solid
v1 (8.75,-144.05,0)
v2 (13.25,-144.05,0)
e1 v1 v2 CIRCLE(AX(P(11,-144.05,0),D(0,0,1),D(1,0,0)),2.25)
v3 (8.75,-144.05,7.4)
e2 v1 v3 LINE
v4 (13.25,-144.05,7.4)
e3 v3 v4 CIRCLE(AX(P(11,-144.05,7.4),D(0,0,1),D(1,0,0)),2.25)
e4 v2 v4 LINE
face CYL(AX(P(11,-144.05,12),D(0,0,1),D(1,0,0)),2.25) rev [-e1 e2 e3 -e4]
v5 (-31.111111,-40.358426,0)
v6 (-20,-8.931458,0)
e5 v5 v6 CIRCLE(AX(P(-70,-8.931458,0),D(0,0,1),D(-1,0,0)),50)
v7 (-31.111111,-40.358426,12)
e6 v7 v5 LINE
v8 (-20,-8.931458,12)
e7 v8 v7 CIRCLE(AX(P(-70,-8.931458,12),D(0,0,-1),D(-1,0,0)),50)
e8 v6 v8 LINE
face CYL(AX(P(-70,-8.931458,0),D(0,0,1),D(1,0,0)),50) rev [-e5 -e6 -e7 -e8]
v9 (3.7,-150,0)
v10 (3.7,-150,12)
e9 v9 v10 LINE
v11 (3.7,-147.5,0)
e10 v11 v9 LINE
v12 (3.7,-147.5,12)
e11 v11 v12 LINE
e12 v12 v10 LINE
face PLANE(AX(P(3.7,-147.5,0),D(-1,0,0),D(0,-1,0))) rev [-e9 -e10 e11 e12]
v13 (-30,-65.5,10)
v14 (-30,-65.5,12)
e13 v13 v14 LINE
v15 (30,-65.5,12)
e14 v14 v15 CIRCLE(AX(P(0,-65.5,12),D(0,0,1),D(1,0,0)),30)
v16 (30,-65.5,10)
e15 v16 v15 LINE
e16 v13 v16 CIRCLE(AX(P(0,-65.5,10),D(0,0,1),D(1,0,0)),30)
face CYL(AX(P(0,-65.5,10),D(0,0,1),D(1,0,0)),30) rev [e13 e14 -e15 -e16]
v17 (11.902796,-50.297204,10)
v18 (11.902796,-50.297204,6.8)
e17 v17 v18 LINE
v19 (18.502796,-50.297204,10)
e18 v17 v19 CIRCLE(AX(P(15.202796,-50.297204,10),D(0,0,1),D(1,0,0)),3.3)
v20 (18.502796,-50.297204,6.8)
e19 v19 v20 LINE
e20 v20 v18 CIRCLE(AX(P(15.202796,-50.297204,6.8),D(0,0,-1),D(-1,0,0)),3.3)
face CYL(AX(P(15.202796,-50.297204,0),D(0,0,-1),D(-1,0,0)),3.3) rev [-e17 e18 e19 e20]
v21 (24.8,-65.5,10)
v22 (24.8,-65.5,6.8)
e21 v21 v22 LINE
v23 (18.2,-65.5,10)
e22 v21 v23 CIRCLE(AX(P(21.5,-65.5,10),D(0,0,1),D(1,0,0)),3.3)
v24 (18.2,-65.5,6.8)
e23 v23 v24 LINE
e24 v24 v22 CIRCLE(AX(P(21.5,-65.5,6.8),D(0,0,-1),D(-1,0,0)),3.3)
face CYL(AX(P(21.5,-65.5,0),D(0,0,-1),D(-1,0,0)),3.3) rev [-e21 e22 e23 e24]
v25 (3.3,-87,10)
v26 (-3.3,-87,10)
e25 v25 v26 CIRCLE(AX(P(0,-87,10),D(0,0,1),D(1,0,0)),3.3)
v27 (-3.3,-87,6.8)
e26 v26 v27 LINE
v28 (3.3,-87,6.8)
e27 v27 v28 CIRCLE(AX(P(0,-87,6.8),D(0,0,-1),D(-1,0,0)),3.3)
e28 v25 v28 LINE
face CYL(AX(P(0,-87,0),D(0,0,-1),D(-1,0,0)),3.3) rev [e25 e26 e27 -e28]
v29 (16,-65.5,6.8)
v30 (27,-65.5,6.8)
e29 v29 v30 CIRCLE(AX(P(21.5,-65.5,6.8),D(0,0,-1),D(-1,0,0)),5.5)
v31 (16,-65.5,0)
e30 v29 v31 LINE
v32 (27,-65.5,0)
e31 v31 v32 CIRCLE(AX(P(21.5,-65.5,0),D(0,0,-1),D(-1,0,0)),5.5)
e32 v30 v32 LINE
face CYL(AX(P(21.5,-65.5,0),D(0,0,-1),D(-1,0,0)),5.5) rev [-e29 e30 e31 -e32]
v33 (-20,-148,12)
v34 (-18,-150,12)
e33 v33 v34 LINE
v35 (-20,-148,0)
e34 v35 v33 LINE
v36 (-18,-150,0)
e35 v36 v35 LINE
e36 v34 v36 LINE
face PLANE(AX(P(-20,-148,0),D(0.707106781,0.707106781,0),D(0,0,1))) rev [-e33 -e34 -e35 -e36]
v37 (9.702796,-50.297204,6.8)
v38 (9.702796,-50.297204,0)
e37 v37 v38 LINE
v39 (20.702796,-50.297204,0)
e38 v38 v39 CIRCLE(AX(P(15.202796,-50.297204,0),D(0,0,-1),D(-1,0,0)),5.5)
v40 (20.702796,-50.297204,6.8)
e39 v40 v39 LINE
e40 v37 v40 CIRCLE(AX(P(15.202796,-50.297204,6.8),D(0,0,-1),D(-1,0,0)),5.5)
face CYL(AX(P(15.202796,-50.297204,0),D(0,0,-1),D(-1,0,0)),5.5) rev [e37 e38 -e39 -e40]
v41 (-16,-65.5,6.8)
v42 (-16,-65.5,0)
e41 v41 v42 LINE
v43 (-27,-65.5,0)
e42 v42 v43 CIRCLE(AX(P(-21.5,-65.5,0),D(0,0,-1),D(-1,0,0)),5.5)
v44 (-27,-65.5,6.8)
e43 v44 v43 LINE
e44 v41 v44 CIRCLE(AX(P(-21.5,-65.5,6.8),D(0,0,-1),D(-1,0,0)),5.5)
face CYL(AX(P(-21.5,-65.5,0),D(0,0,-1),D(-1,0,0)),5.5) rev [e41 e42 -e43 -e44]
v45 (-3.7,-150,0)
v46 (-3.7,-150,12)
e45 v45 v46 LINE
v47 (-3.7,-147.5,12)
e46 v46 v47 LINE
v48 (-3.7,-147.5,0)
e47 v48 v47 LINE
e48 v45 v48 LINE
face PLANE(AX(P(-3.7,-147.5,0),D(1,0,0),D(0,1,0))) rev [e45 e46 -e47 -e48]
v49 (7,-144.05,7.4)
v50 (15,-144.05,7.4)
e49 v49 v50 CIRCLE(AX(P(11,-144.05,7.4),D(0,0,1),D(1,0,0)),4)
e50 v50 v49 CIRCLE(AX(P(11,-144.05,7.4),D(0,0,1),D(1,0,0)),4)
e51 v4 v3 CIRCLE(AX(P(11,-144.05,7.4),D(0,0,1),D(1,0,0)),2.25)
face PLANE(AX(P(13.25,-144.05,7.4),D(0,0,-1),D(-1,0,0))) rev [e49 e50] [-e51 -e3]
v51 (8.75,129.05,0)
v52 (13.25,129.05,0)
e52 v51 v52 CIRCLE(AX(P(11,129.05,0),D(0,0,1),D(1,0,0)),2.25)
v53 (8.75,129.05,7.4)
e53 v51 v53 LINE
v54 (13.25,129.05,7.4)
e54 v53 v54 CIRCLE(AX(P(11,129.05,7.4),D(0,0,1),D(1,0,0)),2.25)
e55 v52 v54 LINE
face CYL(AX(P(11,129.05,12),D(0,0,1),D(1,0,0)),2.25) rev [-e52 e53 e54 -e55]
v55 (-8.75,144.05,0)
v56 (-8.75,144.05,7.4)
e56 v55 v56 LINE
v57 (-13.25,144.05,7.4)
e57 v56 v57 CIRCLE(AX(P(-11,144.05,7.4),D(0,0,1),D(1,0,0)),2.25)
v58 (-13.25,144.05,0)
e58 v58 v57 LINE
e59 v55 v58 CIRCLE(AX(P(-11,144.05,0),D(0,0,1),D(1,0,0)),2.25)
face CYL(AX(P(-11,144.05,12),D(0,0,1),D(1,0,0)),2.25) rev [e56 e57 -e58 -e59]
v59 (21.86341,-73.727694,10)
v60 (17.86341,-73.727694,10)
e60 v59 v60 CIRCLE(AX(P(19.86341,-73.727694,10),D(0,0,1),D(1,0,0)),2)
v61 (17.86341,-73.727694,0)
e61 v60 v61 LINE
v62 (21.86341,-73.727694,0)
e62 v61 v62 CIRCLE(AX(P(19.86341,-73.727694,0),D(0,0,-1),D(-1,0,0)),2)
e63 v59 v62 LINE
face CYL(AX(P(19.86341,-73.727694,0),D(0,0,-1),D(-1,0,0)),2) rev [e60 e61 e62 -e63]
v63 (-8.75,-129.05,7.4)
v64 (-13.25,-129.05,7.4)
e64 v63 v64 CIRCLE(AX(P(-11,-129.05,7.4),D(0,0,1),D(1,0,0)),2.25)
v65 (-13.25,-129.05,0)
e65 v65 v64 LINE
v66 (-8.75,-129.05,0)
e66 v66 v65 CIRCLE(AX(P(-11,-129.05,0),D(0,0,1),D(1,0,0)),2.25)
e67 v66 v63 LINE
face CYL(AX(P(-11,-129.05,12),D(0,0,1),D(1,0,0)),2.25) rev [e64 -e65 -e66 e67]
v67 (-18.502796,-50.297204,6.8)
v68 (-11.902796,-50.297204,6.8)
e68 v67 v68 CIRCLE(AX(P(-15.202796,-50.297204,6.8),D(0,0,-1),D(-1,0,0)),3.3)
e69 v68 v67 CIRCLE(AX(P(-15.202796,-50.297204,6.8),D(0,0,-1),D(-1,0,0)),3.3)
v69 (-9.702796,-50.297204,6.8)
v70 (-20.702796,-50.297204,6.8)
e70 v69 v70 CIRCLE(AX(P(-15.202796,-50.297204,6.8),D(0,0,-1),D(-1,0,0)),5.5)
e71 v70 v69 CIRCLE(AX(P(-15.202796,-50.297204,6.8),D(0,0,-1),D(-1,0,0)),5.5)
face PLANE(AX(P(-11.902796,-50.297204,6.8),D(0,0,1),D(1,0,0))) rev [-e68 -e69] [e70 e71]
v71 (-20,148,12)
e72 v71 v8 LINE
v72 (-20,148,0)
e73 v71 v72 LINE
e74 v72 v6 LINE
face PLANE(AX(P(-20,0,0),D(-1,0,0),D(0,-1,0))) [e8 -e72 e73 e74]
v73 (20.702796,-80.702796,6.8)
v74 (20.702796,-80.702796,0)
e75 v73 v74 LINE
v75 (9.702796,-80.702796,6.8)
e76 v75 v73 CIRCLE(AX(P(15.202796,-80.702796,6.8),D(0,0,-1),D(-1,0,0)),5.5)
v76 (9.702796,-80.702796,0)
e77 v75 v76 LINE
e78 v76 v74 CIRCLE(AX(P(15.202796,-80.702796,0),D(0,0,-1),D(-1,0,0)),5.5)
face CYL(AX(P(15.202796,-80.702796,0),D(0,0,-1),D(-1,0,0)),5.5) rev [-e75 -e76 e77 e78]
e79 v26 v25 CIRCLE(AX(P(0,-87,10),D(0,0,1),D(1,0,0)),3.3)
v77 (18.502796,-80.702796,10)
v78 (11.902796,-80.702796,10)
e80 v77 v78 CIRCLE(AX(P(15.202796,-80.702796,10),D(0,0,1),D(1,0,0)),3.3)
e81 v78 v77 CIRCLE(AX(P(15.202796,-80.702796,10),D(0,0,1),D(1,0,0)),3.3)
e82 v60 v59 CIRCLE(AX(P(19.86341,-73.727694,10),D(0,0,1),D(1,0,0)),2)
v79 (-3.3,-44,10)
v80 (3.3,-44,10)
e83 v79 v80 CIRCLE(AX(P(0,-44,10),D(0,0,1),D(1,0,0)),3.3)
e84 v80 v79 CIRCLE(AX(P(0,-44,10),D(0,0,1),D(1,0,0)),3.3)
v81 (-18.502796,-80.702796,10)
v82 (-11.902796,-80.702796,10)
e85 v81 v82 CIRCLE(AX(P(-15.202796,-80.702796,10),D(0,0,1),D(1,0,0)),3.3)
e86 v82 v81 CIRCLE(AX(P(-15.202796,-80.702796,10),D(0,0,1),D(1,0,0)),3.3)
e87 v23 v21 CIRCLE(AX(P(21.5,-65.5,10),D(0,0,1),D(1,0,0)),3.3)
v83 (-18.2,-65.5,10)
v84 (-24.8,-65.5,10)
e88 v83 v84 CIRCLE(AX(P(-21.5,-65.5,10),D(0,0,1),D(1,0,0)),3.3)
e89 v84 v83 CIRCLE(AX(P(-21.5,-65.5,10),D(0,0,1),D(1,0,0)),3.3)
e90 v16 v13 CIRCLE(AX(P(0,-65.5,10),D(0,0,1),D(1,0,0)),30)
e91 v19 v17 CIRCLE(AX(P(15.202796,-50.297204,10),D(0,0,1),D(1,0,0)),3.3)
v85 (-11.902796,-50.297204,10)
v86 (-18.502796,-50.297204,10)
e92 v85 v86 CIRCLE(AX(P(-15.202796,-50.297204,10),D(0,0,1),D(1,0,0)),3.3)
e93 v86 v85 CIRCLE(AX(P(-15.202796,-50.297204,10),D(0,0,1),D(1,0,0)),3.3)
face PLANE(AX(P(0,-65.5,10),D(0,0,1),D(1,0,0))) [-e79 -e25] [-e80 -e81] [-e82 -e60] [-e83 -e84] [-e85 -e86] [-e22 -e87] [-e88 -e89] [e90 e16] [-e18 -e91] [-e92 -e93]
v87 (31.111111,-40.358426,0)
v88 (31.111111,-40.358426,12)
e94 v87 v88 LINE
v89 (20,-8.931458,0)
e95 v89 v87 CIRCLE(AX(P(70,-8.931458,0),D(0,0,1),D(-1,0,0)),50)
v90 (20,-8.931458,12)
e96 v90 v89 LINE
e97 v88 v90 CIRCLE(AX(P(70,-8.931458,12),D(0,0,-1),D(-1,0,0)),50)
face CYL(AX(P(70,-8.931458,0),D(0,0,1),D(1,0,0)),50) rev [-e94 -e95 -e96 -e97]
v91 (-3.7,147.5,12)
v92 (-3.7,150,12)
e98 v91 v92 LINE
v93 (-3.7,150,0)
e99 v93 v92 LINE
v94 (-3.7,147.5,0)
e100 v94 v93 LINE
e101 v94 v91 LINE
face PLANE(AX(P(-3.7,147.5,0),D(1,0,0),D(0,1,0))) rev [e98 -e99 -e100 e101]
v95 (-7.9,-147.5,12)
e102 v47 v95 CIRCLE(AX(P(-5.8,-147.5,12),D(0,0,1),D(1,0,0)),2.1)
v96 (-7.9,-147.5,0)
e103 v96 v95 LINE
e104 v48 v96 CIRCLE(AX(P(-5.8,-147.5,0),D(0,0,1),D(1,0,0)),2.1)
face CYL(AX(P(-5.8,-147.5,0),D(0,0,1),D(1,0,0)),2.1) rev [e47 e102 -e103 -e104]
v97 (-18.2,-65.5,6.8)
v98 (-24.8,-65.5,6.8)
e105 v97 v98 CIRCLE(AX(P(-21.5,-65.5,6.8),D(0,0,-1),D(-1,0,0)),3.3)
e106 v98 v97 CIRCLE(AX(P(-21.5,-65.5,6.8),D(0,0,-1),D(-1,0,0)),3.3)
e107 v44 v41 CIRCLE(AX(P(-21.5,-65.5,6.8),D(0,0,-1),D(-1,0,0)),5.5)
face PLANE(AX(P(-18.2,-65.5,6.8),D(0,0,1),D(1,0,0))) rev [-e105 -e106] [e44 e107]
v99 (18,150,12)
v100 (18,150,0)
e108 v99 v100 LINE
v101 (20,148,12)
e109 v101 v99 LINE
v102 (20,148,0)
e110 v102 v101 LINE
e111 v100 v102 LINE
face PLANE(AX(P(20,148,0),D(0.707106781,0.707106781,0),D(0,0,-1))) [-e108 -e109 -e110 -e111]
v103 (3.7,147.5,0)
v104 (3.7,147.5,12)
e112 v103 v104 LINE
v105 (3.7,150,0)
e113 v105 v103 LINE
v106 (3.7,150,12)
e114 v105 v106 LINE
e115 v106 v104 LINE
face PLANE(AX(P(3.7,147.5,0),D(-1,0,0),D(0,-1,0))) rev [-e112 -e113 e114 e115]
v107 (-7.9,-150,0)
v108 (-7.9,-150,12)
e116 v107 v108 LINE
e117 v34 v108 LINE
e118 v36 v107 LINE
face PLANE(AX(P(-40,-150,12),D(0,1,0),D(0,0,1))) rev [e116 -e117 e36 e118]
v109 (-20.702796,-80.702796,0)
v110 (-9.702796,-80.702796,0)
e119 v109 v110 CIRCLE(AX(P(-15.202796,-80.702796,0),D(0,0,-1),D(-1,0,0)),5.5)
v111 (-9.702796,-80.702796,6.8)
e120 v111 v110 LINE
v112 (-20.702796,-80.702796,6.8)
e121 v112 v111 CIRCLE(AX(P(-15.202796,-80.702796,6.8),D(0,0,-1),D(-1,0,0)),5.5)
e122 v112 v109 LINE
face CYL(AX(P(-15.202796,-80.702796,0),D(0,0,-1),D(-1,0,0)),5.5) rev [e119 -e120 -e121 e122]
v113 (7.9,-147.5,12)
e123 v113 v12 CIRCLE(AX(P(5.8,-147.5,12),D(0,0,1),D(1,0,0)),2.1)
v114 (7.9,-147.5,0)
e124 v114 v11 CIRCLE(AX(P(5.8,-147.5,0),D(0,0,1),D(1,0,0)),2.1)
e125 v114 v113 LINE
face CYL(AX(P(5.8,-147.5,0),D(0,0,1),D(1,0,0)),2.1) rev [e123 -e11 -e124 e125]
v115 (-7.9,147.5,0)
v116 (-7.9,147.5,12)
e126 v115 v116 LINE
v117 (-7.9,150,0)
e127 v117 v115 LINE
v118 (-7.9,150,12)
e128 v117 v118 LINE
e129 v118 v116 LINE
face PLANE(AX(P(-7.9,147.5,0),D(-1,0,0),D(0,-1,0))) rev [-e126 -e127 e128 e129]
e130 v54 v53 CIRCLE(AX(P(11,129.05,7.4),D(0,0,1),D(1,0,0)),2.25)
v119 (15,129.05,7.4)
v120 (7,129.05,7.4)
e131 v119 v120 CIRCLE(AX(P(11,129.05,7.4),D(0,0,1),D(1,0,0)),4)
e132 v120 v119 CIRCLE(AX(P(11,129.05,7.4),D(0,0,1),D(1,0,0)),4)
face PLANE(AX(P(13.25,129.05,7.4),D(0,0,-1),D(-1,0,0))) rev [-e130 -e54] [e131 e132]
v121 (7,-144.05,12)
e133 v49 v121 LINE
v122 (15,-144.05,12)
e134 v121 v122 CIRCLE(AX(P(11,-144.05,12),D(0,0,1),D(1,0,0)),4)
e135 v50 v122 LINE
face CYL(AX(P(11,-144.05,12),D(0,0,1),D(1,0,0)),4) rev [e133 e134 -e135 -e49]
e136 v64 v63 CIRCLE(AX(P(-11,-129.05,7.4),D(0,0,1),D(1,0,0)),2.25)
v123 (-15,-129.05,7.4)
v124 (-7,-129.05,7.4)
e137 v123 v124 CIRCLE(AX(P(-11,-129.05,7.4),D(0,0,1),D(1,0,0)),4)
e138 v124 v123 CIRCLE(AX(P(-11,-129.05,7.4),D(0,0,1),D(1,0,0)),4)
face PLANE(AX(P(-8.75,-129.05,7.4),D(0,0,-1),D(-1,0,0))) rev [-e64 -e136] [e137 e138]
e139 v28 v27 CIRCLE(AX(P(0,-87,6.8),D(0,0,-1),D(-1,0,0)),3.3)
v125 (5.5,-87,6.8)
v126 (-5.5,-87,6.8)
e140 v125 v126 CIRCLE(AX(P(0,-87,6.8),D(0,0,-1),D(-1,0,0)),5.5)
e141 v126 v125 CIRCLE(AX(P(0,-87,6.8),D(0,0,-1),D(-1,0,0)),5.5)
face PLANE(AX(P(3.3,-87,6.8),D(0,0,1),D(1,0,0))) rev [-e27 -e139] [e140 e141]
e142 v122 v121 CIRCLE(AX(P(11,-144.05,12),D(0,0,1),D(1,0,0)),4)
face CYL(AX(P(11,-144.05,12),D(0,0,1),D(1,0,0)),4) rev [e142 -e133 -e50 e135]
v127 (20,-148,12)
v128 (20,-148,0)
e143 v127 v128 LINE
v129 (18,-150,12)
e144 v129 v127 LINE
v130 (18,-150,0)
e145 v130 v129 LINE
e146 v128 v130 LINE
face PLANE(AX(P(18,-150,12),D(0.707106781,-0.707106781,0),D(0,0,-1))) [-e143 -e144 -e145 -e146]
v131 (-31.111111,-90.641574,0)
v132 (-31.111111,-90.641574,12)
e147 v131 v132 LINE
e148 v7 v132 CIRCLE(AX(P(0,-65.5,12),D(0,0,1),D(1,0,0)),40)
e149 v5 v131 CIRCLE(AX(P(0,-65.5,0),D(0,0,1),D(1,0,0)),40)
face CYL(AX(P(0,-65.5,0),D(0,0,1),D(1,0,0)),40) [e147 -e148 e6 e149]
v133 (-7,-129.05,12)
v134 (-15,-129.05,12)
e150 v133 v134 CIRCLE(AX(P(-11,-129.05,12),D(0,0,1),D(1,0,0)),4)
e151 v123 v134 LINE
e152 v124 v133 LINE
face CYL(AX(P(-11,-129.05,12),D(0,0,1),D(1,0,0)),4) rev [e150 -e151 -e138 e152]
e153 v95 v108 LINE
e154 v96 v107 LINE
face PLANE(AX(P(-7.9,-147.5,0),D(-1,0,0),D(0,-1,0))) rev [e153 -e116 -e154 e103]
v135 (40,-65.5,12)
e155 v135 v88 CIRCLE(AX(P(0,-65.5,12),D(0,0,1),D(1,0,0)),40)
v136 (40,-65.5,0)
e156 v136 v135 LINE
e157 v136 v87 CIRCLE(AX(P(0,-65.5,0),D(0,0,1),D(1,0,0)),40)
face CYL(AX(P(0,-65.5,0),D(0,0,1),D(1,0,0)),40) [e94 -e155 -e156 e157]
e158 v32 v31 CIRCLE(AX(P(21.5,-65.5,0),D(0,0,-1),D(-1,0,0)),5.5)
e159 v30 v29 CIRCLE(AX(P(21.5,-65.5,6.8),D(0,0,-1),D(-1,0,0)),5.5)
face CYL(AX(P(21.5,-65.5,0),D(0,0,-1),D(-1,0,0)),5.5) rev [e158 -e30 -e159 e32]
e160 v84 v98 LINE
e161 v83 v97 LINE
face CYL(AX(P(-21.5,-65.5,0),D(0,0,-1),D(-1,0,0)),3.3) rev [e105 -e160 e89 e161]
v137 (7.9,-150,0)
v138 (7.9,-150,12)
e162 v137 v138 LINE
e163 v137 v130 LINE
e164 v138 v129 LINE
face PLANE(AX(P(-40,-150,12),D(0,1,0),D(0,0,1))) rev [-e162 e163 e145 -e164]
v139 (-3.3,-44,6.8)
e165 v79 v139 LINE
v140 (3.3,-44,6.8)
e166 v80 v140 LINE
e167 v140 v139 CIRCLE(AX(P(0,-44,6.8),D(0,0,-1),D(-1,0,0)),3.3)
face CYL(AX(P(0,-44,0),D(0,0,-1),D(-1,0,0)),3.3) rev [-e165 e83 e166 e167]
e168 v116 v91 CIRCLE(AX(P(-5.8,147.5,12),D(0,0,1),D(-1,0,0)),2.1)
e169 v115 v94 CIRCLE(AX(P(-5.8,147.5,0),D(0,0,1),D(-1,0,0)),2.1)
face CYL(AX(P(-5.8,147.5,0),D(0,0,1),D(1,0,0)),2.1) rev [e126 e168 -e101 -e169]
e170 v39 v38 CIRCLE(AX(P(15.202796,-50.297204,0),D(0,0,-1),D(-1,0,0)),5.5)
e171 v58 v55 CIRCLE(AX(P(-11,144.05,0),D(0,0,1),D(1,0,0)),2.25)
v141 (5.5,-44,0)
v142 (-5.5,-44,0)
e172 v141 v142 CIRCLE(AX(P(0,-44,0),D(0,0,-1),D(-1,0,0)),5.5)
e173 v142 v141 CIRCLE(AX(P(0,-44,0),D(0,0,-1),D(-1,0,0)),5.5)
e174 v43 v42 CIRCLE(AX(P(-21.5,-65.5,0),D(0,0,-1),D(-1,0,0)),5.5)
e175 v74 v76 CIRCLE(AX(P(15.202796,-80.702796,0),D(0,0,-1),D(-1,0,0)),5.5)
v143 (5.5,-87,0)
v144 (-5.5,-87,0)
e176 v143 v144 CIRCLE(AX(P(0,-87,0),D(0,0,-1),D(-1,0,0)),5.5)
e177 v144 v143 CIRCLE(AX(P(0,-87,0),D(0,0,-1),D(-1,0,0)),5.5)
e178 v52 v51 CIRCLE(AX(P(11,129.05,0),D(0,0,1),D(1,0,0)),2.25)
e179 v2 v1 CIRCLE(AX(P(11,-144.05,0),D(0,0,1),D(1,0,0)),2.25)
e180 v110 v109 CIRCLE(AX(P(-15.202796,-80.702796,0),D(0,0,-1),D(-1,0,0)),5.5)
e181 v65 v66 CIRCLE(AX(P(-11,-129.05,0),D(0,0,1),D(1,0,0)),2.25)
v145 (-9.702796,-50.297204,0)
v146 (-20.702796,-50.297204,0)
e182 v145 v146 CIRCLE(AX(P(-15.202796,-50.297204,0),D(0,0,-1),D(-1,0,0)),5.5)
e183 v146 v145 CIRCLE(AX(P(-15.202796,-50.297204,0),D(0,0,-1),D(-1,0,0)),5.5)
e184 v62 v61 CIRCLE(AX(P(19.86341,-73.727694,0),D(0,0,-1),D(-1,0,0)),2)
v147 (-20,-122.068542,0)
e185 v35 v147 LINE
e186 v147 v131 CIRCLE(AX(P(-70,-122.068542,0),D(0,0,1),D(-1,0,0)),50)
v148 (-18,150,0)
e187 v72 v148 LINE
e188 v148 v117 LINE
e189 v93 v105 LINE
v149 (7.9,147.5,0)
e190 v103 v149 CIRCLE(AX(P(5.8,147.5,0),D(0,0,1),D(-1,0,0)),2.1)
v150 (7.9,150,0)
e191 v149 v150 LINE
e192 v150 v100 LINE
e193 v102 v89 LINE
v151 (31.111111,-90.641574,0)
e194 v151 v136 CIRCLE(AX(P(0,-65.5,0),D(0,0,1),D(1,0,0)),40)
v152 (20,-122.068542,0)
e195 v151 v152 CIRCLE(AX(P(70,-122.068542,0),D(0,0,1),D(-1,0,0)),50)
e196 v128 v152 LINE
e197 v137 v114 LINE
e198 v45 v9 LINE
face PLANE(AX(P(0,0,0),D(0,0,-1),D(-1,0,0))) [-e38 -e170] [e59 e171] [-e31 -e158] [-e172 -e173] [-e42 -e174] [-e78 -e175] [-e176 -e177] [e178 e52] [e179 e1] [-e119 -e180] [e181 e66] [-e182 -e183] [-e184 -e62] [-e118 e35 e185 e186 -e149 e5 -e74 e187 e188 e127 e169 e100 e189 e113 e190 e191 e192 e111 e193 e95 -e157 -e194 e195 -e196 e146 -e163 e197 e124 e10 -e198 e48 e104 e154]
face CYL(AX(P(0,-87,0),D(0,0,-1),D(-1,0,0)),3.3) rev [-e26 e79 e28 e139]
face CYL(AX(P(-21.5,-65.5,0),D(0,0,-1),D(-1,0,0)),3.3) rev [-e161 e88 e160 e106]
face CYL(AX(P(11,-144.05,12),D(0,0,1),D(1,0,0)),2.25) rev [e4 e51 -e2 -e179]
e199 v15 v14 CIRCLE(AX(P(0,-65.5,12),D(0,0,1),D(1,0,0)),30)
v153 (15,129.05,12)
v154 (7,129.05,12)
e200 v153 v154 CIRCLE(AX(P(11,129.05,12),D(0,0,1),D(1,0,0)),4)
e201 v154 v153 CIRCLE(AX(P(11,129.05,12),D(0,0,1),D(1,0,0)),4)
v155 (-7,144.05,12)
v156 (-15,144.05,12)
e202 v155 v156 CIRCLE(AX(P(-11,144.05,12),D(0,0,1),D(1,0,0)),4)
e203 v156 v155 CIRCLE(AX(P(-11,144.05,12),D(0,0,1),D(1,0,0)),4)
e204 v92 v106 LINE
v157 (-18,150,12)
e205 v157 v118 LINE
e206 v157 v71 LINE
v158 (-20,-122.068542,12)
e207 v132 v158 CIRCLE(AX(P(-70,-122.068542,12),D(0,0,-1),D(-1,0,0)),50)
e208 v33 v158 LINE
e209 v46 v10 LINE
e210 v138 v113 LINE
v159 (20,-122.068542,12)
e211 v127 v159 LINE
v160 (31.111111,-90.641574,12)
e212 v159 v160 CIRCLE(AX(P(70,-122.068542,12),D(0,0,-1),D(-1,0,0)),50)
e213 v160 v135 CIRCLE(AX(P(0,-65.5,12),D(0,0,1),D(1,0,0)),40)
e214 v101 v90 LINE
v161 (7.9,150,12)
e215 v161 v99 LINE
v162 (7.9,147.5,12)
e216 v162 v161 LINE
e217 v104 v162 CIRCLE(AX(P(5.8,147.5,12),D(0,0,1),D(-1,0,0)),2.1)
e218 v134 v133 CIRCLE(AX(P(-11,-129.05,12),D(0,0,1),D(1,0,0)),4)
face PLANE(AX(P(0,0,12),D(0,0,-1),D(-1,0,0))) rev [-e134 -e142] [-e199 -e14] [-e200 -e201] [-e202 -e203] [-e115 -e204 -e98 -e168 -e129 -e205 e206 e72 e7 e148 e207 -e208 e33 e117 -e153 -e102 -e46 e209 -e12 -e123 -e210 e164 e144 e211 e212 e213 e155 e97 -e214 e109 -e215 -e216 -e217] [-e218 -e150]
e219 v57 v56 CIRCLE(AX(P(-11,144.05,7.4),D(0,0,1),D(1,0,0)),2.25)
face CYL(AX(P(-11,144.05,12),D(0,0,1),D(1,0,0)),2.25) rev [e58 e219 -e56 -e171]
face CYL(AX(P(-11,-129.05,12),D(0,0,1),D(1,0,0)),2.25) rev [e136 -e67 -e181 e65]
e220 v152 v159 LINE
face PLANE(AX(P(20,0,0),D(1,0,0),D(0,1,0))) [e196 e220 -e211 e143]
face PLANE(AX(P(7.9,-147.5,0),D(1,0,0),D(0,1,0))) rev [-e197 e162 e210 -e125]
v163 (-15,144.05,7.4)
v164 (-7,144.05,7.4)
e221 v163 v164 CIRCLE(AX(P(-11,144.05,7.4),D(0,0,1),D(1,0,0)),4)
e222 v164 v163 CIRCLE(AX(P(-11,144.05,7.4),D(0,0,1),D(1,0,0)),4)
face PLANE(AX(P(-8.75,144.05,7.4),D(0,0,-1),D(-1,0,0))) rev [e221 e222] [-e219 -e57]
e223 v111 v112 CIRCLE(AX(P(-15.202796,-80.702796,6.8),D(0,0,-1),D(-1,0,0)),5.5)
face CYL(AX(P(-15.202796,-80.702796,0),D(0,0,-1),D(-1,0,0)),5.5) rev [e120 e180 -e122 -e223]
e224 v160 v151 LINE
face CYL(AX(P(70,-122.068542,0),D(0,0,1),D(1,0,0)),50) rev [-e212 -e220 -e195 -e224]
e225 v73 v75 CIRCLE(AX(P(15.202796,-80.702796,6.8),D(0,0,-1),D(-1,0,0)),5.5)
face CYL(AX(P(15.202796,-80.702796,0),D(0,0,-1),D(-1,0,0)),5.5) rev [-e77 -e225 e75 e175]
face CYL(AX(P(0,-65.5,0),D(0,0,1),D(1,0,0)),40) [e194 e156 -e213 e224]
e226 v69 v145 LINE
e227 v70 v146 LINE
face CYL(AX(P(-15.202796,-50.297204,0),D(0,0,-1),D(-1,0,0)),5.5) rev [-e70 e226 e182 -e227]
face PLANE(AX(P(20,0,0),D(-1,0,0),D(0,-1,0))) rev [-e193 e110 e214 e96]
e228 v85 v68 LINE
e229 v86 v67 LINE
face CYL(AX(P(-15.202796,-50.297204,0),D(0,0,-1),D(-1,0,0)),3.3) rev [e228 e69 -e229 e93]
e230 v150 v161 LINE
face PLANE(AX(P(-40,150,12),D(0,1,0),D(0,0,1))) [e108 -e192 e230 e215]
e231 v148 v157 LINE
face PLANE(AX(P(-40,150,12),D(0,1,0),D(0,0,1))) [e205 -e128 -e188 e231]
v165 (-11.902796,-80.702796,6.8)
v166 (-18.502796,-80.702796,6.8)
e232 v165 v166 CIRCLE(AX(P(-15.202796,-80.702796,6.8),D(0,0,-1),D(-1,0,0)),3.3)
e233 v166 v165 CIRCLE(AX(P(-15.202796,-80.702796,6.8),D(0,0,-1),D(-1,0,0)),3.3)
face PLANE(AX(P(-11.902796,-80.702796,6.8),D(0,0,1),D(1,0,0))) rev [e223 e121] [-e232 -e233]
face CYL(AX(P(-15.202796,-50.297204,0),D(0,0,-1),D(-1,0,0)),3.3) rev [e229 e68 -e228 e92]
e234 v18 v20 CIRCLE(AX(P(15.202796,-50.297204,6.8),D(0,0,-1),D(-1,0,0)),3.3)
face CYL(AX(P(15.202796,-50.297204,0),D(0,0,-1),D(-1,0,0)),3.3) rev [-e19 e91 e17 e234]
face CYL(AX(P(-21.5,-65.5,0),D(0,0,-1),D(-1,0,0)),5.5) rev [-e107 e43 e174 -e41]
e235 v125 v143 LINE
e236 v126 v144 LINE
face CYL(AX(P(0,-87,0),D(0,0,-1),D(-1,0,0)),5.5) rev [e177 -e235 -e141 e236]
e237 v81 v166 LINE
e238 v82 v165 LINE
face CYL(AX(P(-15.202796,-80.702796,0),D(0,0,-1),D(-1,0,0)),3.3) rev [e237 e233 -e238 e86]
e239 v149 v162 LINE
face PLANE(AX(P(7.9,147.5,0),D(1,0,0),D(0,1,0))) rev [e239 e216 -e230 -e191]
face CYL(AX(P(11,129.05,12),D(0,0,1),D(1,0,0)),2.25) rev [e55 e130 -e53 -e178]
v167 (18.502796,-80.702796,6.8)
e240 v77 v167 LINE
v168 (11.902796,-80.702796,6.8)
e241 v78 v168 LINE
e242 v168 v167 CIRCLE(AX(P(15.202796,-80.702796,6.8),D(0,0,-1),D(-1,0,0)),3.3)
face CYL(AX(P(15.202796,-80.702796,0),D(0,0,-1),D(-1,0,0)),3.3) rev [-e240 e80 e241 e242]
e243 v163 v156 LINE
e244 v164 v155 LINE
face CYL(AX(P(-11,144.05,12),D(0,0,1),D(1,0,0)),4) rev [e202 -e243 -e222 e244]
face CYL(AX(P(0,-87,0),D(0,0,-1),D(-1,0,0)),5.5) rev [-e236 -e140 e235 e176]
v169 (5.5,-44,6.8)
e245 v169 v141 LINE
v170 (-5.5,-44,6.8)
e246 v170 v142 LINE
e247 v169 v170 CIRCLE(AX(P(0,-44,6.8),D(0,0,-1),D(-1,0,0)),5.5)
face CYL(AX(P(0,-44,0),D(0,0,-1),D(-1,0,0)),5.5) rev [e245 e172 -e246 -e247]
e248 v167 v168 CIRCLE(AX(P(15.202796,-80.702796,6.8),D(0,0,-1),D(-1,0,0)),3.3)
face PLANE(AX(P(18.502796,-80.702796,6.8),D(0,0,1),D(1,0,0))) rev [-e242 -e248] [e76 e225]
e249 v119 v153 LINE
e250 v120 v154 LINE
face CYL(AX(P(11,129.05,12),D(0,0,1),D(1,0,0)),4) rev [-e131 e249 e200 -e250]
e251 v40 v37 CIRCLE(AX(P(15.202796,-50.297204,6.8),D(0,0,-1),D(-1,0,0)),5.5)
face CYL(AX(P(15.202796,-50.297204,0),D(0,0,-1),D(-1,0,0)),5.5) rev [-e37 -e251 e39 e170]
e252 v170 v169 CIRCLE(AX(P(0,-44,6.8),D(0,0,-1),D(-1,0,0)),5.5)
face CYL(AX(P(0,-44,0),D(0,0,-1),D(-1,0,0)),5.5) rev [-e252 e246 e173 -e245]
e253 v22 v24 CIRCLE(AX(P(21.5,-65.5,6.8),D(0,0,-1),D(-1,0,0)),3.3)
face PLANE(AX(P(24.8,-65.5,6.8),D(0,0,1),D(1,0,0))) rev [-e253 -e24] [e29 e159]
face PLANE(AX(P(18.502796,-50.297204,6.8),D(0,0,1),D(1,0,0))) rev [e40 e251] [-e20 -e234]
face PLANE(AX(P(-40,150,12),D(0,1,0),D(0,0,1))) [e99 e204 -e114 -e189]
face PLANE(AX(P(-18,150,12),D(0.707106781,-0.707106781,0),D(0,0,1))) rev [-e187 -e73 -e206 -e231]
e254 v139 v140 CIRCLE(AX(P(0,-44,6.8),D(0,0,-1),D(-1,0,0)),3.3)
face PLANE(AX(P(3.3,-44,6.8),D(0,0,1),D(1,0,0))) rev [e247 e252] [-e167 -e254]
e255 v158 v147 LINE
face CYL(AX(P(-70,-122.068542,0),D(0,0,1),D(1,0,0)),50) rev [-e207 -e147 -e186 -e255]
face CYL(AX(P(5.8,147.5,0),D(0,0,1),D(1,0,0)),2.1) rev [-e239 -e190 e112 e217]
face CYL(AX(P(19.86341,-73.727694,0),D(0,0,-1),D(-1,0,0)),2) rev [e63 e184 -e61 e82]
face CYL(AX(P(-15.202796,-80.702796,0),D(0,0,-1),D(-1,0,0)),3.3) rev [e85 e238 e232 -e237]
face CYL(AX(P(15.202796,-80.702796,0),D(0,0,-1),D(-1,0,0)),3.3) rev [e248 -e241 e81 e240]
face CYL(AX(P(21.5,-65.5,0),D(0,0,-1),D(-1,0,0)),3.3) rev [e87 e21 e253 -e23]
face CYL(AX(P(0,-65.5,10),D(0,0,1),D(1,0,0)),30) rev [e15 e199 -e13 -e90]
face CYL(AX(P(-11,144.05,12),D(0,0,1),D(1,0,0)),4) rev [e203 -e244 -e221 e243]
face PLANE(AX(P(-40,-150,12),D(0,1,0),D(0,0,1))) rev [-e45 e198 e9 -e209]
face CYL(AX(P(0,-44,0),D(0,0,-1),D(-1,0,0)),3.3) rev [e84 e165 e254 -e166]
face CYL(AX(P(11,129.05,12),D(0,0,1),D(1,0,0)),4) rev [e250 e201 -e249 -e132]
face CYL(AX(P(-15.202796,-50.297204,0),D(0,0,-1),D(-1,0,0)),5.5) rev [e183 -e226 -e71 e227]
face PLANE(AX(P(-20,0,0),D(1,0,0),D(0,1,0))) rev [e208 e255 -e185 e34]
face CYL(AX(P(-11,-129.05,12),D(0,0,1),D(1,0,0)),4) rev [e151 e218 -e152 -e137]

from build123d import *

# Parameters (mm, degrees)
SKETCH_1_W                   = 80
SKETCH_1_H                   = 300
EXTRUDE_1_DEPTH              = 12
CHAMFER_1_SIZE               = 2
SKETCH_2_R                   = 30
CUT_EXTRUDE_1_DEPTH          = 2
CUT_EXTRUDE_2_DEPTH          = 156.704848993
FILLET_1_R                   = 50
CHAMFER_3_SIZE               = 2
HOLE_WIZARD_M6_1_D           = 6.6
HOLE_WIZARD_M6_1_CBORE_D     = 11
HOLE_WIZARD_M6_1_CBORE_DEPTH = 6.8
F_4_0MM_1_D                  = 4
HOLE_WIZARD_M4_1_D           = 4.5
HOLE_WIZARD_M4_1_CBORE_D     = 8
HOLE_WIZARD_M4_1_CBORE_DEPTH = 4.6
CUT_EXTRUDE_3_DEPTH          = 156.704848993
PATTERN_CIRCULAR_1_COUNT     = 8


with BuildPart() as part:
    # 草图1 → 凸台-拉伸1 (new body)
    with BuildSketch(Plane.XY):
        Rectangle(SKETCH_1_W, SKETCH_1_H)
    extrude(amount=EXTRUDE_1_DEPTH)

    # 倒角1
    chamfer_1_edges = [part.edges().sort_by_distance(p)[0] for p in [
        (-40, -150, 6),
        (40, -150, 6),
        (40, 150, 6),
        (-40, 150, 6),
    ]]
    chamfer(chamfer_1_edges, length=CHAMFER_1_SIZE)

    # 草图2 → 切除-拉伸1 (cut)
    with BuildSketch(Plane.XY.offset(12)):
        with Locations((0, -65.5)):
            Circle(SKETCH_2_R)
    extrude(amount=-CUT_EXTRUDE_1_DEPTH, mode=Mode.SUBTRACT)

    # 草图3 → 切除-拉伸2 (cut, through all)
    with BuildSketch(Plane.XY.offset(12)):
        with BuildLine():
            Line((-38, -150), (-20, -150))
            Line((-20, -150), (-20, -100.141016151))
            ThreePointArc((-20, -100.141016151), (-34.641016151, -85.5), (-40, -65.5))
            Line((-40, -65.5), (-40, -148))
            Line((-40, -148), (-38, -150))
        make_face()
        with BuildLine():
            Line((20, -100.141016151), (20, -150))
            Line((20, -150), (38, -150))
            Line((38, -150), (40, -148))
            Line((40, -148), (40, -65.5))
            ThreePointArc((40, -65.5), (34.641016151, -85.5), (20, -100.141016151))
        make_face()
        with BuildLine():
            Line((-40, 148), (-40, -65.5))
            ThreePointArc((-40, -65.5), (-34.641016151, -45.5), (-20, -30.858983849))
            Line((-20, -30.858983849), (-20, 150))
            Line((-20, 150), (-38, 150))
            Line((-38, 150), (-40, 148))
        make_face()
        with BuildLine():
            ThreePointArc((20, -30.858983849), (34.641016151, -45.5), (40, -65.5))
            Line((40, -65.5), (40, 148))
            Line((40, 148), (38, 150))
            Line((38, 150), (20, 150))
            Line((20, 150), (20, -30.858983849))
        make_face()
    extrude(amount=-CUT_EXTRUDE_2_DEPTH, mode=Mode.SUBTRACT)

    # 圆角1
    fillet_1_edges = [part.edges().sort_by_distance(p)[0] for p in [
        (20, -30.858983849, 6),
        (-20, -30.858983849, 6),
        (-20, -100.141016151, 6),
        (20, -100.141016151, 6),
    ]]
    fillet(fillet_1_edges, radius=FILLET_1_R)

    # 倒角3
    chamfer_3_edges = [part.edges().sort_by_distance(p)[0] for p in [
        (20, -150, 6),
        (20, 150, 6),
        (-20, 150, 6),
        (-20, -150, 6),
    ]]
    chamfer(chamfer_3_edges, length=CHAMFER_3_SIZE)

    # M6 六角圆柱头螺钉的柱形沉头孔1 (through all)
    with Locations(Plane(origin=(0, 0, 0), x_dir=(-1, 0, 0), z_dir=(0, 0, -1))):
        with Locations((0, -87)):
            hole_wizard_m6_1 = CounterBoreHole(HOLE_WIZARD_M6_1_D / 2, HOLE_WIZARD_M6_1_CBORE_D / 2, HOLE_WIZARD_M6_1_CBORE_DEPTH)

    # Ø4.0mm 暗销孔1 (through all)
    with Locations(Plane(origin=(0, 0, 0), x_dir=(-1, 0, 0), z_dir=(0, 0, -1))):
        with Locations((-19.863409949, -73.727693796)):
            Hole(F_4_0MM_1_D / 2)

    # M4 六角圆柱头螺钉的柱形沉头孔1 (through all)
    with Locations(Plane.XY.offset(12)):
        with Locations((-11, -129.05), (11, -144.05), (-11, 144.05), (11, 129.05)):
            CounterBoreHole(HOLE_WIZARD_M4_1_D / 2, HOLE_WIZARD_M4_1_CBORE_D / 2, HOLE_WIZARD_M4_1_CBORE_DEPTH)

    # 草图14 → 切除-拉伸3 (cut, through all)
    with BuildSketch(Plane.XY.offset(12)):
        with BuildLine():
            Line((7.9, -147.5), (7.9, -150))
            ThreePointArc((7.9, -150), (5.8, -152.1), (3.7, -150))
            Line((3.7, -150), (3.7, -147.5))
            ThreePointArc((3.7, -147.5), (5.8, -145.4), (7.9, -147.5))
        make_face()
        with BuildLine():
            Line((-3.7, -147.5), (-3.7, -150))
            ThreePointArc((-3.7, -150), (-5.8, -152.1), (-7.9, -150))
            Line((-7.9, -150), (-7.9, -147.5))
            ThreePointArc((-7.9, -147.5), (-5.8, -145.4), (-3.7, -147.5))
        make_face()
        with BuildLine():
            Line((7.9, 147.5), (7.9, 150))
            ThreePointArc((7.9, 150), (5.8, 152.1), (3.7, 150))
            Line((3.7, 150), (3.7, 147.5))
            ThreePointArc((3.7, 147.5), (5.8, 145.4), (7.9, 147.5))
        make_face()
        with BuildLine():
            Line((-3.7, 147.5), (-3.7, 150))
            ThreePointArc((-3.7, 150), (-5.8, 152.1), (-7.9, 150))
            Line((-7.9, 150), (-7.9, 147.5))
            ThreePointArc((-7.9, 147.5), (-5.8, 145.4), (-3.7, 147.5))
        make_face()
    extrude(amount=-CUT_EXTRUDE_3_DEPTH, mode=Mode.SUBTRACT)

    # 阵列(圆周)1: M6 六角圆柱头螺钉的柱形沉头孔1 ×8 about axis
    pattern_circular_1_axis = Axis((0, -65.5, 0), (0, 0, 1))
    for i in range(1, PATTERN_CIRCULAR_1_COUNT):
        add(hole_wizard_m6_1.rotate(pattern_circular_1_axis, i * 360 / PATTERN_CIRCULAR_1_COUNT), mode=Mode.SUBTRACT)


solid = part.part
